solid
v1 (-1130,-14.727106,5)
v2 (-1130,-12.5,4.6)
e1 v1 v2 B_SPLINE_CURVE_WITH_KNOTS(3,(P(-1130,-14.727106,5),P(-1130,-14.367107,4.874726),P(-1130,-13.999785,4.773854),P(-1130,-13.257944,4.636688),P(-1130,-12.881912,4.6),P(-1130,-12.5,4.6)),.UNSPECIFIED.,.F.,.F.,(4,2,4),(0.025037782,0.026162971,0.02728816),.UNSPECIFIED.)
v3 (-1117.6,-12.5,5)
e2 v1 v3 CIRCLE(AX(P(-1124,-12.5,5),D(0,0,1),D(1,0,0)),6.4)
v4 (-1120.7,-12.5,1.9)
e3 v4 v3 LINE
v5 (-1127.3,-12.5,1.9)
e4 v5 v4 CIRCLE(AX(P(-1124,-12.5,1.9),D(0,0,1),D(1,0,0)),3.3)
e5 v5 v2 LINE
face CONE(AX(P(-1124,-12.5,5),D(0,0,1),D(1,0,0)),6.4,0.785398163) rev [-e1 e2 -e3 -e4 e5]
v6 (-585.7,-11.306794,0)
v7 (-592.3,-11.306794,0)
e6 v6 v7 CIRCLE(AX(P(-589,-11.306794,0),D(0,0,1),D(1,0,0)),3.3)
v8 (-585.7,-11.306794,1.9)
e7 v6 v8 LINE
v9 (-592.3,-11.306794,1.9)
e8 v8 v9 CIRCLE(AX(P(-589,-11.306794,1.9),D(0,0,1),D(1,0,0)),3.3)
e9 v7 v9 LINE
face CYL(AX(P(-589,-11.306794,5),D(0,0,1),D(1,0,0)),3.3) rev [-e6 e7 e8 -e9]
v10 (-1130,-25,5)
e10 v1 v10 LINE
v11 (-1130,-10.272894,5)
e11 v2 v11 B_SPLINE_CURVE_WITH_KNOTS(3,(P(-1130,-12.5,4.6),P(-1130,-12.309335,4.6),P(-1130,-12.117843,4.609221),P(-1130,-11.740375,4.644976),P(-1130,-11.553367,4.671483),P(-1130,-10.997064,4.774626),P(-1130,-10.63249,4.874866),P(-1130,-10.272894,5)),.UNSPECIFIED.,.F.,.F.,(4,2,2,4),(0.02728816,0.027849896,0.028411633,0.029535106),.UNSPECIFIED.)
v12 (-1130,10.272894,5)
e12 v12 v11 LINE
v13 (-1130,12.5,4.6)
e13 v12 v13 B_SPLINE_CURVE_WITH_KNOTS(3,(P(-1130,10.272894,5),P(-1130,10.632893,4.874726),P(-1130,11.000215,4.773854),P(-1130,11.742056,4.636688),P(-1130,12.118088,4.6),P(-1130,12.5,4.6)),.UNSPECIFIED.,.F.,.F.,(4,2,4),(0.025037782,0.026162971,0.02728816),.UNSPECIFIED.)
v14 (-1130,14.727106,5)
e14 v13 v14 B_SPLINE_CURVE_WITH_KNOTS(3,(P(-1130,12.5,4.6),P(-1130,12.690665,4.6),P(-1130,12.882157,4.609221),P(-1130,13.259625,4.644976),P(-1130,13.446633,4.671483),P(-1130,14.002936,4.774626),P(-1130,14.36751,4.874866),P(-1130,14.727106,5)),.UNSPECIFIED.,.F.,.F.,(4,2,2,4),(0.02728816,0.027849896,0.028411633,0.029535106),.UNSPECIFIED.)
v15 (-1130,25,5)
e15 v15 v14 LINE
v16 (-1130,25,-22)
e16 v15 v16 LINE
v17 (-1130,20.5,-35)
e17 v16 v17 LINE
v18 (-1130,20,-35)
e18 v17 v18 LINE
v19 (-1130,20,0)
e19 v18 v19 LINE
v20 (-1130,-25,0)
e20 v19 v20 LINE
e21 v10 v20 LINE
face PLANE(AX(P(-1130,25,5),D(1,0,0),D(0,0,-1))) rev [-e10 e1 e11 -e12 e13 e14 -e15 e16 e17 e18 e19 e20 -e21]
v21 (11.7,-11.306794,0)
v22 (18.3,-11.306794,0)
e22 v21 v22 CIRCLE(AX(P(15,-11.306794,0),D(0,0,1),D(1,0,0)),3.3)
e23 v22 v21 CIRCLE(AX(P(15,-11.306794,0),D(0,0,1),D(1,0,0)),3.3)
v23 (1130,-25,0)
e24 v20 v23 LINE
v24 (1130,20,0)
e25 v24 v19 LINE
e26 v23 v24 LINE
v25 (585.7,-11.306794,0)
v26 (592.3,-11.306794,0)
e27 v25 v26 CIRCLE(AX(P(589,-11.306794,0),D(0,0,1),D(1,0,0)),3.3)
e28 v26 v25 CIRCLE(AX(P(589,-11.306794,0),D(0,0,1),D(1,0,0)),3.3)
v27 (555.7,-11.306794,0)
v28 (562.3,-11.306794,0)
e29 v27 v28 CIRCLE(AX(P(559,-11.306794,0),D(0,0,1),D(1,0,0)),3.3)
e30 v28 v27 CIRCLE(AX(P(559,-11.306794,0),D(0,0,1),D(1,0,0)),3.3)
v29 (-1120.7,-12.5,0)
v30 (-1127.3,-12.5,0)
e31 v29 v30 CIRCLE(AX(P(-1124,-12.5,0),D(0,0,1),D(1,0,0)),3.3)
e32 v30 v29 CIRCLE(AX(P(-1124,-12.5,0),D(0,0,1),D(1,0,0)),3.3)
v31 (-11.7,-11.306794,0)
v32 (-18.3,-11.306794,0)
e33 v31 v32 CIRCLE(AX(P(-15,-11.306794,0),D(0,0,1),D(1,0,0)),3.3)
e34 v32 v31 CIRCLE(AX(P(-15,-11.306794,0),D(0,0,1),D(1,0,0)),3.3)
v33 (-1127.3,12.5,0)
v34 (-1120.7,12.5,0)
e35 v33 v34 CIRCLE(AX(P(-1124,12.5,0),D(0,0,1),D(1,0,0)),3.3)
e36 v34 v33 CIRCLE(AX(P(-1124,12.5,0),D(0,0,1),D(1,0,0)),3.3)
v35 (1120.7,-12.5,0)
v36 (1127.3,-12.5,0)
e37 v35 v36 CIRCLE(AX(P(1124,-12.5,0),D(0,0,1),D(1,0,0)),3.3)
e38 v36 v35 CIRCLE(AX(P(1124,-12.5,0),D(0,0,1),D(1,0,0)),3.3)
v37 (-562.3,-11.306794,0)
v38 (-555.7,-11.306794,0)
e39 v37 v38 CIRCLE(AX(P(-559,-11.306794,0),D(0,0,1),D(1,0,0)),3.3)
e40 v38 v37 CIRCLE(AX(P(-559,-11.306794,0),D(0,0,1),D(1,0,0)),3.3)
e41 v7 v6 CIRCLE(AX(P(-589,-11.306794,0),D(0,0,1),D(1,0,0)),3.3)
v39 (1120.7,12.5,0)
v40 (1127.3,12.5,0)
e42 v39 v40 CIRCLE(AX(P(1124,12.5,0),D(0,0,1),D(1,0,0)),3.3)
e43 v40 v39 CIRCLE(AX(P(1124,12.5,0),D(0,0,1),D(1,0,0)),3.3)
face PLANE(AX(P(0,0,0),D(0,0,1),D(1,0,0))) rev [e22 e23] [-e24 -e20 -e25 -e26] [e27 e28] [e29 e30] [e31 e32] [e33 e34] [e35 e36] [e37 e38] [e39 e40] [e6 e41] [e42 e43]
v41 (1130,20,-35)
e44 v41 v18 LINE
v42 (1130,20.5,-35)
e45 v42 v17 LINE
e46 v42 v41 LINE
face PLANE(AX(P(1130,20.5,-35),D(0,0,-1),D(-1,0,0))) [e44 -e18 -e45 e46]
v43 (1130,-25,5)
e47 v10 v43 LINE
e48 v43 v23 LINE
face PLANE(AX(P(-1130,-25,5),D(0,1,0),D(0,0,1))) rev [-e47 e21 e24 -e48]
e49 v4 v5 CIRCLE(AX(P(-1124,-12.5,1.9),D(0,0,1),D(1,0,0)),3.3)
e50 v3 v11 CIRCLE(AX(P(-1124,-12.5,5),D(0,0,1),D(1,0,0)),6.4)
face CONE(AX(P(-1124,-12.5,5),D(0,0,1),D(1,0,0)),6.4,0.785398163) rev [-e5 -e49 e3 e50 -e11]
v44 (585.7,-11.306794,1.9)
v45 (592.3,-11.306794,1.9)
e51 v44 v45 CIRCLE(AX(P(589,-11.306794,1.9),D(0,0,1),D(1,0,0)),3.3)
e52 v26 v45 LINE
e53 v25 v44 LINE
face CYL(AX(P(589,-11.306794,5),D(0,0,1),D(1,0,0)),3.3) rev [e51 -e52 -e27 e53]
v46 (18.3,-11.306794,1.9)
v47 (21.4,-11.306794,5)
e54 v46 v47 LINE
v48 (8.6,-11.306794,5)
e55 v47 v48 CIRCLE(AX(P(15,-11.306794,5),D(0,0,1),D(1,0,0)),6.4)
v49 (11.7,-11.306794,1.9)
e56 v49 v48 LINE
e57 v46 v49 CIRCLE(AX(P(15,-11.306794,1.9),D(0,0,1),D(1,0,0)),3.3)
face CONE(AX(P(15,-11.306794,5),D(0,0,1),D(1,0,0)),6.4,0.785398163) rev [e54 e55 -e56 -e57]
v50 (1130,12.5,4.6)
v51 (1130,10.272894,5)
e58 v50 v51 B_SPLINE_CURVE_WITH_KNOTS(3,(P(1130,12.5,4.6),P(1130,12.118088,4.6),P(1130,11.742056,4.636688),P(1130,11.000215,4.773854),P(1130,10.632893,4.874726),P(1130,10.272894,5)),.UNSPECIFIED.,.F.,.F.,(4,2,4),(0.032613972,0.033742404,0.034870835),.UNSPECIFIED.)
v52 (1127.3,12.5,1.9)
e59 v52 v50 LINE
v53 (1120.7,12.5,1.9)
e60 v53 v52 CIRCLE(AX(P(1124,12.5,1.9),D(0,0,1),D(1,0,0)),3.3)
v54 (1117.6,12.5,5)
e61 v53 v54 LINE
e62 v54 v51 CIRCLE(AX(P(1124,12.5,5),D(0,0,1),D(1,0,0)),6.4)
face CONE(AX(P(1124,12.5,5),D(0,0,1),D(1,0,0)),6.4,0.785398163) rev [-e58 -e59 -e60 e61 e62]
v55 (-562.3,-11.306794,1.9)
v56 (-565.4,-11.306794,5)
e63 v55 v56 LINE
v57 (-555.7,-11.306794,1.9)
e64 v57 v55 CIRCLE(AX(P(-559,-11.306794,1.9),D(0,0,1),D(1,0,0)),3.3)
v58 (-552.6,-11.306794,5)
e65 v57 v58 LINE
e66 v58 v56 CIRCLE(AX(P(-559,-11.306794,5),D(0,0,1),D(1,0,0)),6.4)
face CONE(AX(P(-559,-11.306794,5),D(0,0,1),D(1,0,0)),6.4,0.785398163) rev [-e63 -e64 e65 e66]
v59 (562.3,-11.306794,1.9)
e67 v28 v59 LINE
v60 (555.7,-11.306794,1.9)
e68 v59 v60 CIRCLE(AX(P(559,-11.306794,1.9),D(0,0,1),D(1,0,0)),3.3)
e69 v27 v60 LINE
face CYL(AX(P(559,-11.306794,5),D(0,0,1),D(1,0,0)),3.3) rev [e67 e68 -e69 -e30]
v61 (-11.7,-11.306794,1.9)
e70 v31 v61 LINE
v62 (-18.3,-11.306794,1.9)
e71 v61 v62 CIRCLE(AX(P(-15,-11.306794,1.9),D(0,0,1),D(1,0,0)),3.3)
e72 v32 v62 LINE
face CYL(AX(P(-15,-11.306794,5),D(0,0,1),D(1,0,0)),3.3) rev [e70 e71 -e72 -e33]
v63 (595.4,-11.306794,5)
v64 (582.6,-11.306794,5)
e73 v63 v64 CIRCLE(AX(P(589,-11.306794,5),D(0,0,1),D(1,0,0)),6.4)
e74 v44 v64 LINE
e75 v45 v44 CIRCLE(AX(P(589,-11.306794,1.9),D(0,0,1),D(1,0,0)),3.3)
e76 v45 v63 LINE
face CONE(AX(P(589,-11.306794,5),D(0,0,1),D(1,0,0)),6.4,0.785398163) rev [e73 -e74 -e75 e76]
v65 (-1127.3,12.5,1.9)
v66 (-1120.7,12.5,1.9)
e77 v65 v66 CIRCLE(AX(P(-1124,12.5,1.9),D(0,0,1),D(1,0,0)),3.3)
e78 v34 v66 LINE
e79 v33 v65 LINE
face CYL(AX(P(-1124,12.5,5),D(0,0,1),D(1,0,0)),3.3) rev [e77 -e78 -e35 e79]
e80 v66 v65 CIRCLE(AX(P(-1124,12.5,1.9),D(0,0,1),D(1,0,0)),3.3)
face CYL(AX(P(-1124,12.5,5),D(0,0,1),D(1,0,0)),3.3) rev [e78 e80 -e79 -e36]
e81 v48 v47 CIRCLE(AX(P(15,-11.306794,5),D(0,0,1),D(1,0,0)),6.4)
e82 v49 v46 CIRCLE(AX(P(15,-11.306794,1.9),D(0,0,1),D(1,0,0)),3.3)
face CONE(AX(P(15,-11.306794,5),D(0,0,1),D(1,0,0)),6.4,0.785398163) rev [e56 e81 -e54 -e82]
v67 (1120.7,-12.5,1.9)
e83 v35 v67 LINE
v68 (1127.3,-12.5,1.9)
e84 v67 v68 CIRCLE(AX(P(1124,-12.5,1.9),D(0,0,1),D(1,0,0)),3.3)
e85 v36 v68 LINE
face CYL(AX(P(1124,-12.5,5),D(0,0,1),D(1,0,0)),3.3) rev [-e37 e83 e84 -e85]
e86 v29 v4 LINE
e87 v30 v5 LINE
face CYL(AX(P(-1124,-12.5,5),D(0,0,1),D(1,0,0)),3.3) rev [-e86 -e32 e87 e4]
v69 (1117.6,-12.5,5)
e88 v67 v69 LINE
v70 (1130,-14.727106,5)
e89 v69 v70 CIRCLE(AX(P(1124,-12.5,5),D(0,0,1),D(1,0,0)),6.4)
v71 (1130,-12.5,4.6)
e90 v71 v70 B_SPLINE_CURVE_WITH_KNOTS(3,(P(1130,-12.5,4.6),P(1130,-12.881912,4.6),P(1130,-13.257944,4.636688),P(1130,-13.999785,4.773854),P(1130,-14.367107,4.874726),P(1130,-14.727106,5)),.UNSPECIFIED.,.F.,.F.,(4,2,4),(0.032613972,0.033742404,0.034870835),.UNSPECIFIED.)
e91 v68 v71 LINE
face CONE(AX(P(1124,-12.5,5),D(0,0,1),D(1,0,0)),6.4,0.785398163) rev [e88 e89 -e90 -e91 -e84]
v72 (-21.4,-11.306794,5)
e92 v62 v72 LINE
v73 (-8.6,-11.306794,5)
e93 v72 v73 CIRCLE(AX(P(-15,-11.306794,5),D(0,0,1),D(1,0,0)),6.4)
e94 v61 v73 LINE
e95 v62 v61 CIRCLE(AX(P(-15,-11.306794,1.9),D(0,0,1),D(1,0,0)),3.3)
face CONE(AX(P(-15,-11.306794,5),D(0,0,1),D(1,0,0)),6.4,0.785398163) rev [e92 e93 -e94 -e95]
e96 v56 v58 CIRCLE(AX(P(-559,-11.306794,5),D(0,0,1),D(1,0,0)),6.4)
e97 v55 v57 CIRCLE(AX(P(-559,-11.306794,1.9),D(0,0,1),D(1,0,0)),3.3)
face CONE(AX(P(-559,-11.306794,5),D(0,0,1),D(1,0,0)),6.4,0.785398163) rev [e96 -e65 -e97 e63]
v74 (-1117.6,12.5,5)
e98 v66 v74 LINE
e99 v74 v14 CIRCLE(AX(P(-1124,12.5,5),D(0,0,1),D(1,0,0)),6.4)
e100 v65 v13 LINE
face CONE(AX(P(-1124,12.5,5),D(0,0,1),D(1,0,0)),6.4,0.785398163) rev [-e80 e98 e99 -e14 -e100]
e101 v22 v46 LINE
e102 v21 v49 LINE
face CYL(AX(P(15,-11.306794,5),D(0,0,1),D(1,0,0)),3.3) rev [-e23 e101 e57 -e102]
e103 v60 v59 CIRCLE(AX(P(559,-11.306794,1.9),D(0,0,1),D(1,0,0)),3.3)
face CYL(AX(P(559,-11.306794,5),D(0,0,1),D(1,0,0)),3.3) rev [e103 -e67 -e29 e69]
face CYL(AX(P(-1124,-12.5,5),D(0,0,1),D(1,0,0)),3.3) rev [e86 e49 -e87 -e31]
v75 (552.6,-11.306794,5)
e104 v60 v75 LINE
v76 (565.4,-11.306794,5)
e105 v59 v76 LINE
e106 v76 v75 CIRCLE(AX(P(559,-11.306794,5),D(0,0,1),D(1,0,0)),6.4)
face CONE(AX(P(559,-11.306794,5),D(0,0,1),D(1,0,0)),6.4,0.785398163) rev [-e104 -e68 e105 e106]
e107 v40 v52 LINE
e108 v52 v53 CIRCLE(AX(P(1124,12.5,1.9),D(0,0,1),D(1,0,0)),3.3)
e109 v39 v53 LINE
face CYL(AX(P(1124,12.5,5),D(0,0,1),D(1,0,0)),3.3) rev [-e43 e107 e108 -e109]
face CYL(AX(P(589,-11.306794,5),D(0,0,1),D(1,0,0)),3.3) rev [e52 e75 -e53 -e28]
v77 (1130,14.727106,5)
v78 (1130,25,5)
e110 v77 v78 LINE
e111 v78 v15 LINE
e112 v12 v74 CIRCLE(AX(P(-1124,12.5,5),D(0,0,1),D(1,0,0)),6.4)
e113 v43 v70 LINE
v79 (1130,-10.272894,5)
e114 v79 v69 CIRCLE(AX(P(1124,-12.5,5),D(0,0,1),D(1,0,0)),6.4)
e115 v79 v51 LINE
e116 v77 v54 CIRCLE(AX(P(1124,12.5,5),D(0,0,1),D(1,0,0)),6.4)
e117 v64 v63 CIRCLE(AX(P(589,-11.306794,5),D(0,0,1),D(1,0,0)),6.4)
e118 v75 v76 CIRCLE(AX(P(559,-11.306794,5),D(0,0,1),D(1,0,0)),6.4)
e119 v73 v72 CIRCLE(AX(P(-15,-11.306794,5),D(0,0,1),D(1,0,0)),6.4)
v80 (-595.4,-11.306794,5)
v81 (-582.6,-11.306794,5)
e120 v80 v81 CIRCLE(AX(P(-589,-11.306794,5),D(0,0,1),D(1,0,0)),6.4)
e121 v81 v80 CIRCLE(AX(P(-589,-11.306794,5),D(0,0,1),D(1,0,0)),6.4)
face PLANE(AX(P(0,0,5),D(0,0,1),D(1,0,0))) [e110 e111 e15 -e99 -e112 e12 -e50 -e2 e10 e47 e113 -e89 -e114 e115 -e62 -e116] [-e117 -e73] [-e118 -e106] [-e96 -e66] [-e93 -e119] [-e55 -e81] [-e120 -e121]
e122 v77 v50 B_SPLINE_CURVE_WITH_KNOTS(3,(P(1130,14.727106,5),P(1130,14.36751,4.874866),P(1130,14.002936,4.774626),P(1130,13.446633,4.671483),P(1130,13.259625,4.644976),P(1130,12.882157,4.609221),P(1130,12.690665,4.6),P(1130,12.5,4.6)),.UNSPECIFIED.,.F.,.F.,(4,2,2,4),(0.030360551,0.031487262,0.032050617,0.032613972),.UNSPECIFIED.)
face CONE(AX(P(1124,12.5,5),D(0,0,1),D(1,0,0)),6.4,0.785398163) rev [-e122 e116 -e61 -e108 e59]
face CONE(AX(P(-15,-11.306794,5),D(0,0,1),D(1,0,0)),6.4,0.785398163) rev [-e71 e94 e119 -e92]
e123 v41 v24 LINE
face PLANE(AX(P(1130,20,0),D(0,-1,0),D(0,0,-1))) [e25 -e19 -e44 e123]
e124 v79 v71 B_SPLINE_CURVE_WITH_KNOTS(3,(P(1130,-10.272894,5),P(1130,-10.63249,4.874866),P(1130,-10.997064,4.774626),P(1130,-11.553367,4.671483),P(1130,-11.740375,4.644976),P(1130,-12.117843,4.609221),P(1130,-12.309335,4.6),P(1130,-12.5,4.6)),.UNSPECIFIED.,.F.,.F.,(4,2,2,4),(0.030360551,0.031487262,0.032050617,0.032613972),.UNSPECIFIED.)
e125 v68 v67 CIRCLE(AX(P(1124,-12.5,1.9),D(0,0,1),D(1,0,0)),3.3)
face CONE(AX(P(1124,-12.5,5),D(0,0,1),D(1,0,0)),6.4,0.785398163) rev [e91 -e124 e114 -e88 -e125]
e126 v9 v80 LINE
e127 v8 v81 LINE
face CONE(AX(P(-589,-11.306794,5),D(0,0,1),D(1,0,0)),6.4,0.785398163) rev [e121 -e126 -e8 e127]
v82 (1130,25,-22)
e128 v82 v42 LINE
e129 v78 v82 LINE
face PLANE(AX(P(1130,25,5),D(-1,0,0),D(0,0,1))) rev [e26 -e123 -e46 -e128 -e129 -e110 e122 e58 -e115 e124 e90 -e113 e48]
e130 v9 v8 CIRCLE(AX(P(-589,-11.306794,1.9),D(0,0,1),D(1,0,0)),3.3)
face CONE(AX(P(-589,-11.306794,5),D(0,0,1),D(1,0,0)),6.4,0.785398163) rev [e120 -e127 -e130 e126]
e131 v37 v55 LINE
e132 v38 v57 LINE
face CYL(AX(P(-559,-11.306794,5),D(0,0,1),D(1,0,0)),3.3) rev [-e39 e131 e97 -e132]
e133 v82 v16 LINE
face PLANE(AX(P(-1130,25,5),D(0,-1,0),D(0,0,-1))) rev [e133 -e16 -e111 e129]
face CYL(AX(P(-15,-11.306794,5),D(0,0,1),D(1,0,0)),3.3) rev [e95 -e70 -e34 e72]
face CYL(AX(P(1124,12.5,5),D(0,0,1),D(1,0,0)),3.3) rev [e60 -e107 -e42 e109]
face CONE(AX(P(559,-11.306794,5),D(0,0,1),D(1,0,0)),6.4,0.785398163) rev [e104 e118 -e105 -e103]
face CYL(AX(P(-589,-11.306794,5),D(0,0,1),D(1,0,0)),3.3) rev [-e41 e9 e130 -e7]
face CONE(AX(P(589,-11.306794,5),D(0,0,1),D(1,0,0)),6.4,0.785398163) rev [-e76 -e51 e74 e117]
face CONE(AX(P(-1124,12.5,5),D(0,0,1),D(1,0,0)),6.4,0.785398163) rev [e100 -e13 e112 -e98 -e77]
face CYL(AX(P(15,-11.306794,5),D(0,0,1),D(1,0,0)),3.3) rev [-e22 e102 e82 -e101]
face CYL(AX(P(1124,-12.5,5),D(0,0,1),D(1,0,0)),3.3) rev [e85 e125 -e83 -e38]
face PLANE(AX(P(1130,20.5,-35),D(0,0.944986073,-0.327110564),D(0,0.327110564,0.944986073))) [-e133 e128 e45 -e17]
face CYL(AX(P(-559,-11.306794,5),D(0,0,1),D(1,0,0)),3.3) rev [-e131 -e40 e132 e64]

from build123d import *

# Parameters (mm, degrees)
SKETCH1_W                                            = 2260
SKETCH1_H                                            = 50
BOSS_EXTRUDE1_DEPTH                                  = 5
BOSS_EXTRUDE2_DEPTH                                  = 2260
CSK_FOR_M6_HEXAGON_LOBULAR_SOCKET_RAISED_D           = 6.6
CSK_FOR_M6_HEXAGON_LOBULAR_SOCKET_RAISED_DEPTH       = 19.75
CSK_FOR_M6_HEXAGON_LOBULAR_SOCKET_RAISED_CSINK_D     = 12.8
CSK_FOR_M6_HEXAGON_LOBULAR_SOCKET_RAISED_CSINK_ANGLE = 90
CSK_FOR_M6_HEXAGON_LOBULAR_SOCKET_RAISED_TIP         = 1.982840043


with BuildPart() as part:
    # Sketch1 → Boss-Extrude1 (new body)
    with BuildSketch(Plane.XY):
        Rectangle(SKETCH1_W, SKETCH1_H)
    extrude(amount=BOSS_EXTRUDE1_DEPTH)

    # Sketch2 → Boss-Extrude2 (add)
    with BuildSketch(Plane.ZY.offset(1130)):
        Polygon((0, 25), (-22, 25), (-35, 20.5), (-35, 20), (0, 20), align=None)
    extrude(amount=-BOSS_EXTRUDE2_DEPTH)

    # CSK for M6 Hexagon lobular socket raised CTSK head screws1
    with Locations(Plane.XY.offset(5)):
        with Locations((-589, -11.306794409), (-559, -11.306794409), (-15, -11.306794409), (15, -11.306794409), (559, -11.306794409), (589, -11.306794409), (-1124, -12.5), (-1124, 12.5), (1124, -12.5), (1124, 12.5)):
            CounterSinkHole(CSK_FOR_M6_HEXAGON_LOBULAR_SOCKET_RAISED_D / 2, CSK_FOR_M6_HEXAGON_LOBULAR_SOCKET_RAISED_CSINK_D / 2, depth=CSK_FOR_M6_HEXAGON_LOBULAR_SOCKET_RAISED_DEPTH, counter_sink_angle=CSK_FOR_M6_HEXAGON_LOBULAR_SOCKET_RAISED_CSINK_ANGLE)
            with Locations((0, 0, -(CSK_FOR_M6_HEXAGON_LOBULAR_SOCKET_RAISED_DEPTH + CSK_FOR_M6_HEXAGON_LOBULAR_SOCKET_RAISED_TIP / 2))):  # 118° drill point
                Cone(0, CSK_FOR_M6_HEXAGON_LOBULAR_SOCKET_RAISED_D / 2, CSK_FOR_M6_HEXAGON_LOBULAR_SOCKET_RAISED_TIP, mode=Mode.SUBTRACT)


solid = part.part
